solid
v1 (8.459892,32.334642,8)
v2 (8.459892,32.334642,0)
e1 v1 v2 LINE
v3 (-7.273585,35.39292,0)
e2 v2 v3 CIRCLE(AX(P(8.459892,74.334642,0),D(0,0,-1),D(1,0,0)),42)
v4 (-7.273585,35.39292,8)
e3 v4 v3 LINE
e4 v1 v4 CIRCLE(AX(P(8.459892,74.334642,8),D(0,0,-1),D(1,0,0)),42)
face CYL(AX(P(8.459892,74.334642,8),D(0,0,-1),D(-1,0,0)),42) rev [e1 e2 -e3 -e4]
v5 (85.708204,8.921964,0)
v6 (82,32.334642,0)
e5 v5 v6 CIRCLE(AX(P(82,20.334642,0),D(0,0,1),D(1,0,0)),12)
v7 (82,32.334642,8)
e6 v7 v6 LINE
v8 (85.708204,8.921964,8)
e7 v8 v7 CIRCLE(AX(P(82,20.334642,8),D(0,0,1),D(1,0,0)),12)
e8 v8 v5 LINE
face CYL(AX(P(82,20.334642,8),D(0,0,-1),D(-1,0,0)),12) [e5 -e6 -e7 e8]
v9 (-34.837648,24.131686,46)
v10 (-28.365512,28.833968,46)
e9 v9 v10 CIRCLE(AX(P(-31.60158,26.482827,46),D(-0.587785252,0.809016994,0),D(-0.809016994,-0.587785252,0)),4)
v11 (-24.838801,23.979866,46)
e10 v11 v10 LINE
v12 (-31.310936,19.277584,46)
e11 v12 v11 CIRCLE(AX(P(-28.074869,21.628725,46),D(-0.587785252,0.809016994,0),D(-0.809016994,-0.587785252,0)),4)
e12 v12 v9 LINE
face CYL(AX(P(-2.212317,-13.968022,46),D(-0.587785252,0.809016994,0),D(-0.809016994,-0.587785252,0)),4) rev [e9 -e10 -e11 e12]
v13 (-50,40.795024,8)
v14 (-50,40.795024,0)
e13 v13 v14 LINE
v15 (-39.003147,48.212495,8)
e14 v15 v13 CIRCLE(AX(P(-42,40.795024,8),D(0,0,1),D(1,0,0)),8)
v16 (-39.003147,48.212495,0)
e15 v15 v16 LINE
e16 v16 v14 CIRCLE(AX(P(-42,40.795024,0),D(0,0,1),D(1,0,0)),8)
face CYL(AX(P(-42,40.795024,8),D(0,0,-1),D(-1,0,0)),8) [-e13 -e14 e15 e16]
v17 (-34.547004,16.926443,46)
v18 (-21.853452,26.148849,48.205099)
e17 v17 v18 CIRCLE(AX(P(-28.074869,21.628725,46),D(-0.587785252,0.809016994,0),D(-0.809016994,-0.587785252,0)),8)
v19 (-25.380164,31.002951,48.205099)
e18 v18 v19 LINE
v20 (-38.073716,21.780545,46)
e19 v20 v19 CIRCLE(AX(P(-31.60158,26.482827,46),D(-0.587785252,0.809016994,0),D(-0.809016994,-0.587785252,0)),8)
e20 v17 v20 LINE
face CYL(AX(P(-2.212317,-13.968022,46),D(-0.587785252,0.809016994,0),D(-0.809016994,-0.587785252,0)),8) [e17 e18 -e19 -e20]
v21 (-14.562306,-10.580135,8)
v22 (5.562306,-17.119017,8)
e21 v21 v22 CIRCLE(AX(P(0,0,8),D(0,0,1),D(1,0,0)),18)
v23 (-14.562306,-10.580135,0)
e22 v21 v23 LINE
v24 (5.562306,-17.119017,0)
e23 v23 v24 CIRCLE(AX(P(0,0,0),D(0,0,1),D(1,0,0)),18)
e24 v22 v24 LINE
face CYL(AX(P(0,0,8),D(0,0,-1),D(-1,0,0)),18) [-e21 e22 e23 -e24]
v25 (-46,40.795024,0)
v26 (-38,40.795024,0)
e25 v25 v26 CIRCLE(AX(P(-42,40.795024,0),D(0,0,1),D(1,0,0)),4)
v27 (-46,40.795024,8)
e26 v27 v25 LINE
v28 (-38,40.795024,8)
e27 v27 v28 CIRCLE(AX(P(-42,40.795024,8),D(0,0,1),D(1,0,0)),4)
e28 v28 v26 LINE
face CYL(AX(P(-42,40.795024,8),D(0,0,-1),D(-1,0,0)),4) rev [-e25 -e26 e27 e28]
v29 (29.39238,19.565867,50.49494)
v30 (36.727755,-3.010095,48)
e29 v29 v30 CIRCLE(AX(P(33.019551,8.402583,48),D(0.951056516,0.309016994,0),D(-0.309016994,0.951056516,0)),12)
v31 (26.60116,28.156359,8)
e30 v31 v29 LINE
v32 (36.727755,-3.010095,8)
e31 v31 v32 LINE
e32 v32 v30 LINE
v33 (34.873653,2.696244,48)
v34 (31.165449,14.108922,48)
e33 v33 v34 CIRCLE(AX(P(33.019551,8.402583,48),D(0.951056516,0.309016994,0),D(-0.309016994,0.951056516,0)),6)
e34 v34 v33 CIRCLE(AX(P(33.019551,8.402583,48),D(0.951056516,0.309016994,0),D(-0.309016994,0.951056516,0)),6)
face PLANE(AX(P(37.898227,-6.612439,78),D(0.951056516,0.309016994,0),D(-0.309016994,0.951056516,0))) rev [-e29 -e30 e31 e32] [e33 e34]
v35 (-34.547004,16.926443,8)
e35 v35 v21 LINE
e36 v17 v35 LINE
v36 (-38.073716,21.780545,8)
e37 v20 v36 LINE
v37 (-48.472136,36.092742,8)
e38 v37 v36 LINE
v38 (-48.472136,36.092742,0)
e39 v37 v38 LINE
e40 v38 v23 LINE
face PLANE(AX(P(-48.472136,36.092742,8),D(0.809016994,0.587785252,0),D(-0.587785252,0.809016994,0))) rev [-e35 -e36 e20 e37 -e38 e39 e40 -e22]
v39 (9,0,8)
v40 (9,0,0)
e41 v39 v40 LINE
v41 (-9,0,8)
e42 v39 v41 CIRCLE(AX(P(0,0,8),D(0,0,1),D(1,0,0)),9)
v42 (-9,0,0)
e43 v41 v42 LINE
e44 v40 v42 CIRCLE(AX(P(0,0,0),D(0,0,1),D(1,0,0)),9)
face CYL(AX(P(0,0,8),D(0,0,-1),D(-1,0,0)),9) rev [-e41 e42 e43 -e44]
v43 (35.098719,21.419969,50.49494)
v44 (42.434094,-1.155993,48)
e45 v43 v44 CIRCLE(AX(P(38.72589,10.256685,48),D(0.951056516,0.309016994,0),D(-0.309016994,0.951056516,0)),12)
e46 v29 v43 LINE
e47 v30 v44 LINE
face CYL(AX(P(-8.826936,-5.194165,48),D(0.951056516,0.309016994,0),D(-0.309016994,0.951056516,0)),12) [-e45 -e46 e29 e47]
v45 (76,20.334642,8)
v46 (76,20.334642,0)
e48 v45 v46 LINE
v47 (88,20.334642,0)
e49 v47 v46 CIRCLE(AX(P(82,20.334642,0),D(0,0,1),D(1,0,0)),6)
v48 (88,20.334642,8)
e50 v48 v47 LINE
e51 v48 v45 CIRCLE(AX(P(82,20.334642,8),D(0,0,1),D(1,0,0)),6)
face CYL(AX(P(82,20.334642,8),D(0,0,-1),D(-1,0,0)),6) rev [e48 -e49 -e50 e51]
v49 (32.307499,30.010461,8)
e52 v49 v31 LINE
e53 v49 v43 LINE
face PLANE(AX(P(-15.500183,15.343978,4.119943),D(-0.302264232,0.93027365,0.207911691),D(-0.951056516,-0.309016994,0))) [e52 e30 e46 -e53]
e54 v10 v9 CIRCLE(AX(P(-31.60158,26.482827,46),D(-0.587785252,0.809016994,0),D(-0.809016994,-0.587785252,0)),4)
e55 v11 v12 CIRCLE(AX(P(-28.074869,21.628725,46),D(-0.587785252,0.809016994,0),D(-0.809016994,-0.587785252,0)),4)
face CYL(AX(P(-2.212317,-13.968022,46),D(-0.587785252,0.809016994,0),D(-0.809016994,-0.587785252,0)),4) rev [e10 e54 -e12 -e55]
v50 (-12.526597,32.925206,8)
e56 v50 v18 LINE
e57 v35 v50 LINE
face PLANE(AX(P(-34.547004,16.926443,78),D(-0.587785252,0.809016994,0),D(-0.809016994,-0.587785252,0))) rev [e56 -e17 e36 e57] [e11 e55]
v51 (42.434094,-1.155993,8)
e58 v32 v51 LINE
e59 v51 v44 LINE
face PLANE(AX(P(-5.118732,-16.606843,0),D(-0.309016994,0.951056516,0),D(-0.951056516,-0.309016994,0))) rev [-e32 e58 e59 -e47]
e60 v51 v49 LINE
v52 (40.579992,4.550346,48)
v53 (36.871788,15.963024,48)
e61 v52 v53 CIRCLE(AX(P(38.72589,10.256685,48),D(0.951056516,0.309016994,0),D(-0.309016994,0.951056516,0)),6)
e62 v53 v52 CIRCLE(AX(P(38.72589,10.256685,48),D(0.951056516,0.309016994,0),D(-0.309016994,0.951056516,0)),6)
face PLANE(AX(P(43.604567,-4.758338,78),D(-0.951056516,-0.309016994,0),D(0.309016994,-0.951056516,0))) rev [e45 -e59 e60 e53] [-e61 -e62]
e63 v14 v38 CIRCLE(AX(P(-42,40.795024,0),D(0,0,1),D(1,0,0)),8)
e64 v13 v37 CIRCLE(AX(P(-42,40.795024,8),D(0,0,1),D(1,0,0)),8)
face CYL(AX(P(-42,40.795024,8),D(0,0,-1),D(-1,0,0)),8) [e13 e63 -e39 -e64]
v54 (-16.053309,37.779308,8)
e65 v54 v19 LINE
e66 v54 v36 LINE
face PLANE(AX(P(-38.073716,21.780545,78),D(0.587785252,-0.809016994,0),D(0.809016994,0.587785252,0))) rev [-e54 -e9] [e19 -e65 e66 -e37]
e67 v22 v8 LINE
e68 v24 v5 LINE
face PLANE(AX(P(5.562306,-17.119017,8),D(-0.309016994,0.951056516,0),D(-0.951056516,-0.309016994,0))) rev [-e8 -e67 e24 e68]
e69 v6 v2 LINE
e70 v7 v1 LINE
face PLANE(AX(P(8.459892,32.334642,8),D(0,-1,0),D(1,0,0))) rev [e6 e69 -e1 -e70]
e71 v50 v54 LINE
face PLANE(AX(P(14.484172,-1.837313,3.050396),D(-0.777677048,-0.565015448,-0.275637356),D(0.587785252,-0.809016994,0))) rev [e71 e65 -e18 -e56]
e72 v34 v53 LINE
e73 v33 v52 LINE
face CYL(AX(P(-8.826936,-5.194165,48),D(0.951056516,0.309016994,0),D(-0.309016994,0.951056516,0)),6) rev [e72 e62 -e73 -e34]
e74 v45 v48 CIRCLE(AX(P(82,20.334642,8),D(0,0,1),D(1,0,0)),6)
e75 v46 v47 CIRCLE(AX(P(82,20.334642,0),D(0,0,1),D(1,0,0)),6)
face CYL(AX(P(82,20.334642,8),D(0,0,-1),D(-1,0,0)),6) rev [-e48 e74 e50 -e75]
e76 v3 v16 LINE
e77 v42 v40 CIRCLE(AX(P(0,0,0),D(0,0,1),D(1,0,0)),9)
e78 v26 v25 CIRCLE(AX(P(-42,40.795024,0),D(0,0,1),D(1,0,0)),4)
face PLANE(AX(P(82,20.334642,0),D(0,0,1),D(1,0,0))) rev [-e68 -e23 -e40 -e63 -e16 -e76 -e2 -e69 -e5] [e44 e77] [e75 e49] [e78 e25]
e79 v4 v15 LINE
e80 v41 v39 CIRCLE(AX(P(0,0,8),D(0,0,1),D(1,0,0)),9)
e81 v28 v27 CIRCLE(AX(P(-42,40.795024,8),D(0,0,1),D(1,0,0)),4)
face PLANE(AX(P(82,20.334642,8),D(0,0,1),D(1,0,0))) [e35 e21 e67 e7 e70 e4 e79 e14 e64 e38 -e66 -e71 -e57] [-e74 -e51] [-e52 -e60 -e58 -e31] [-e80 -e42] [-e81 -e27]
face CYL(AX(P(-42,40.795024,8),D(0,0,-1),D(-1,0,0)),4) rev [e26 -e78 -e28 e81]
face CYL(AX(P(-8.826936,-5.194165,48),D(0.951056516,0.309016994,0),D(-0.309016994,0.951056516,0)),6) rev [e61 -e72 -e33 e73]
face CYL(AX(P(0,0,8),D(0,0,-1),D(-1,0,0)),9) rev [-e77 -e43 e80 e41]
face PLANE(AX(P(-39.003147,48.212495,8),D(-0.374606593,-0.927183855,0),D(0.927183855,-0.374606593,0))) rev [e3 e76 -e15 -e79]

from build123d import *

# Parameters (mm, degrees)
BRACKET_PLATE_PROFILE_R    = 9
BRACKET_PLATE_PROFILE_R_2  = 4
BRACKET_PLATE_PROFILE_R_3  = 6
BRACKET_PLATE_8MM_DEPTH    = 8
ARMS_70MM_DEPTH            = 70
GUSSET_TAPER_CUT_PROFILE_R = 6
GUSSET_TAPER_CUT_DEPTH     = 50
ARM_TRIM_CUT_PROFILE_R     = 4
ARM_TRIM_CUT_DEPTH         = 50


with BuildPart() as part:
    # Bracket Plate Profile → Bracket Plate 8mm (new body)
    with BuildSketch(Plane.XY):
        with BuildLine():
            Line((-48.472135955, 36.092742474), (-14.562305899, -10.580134541))
            ThreePointArc((-14.562305899, -10.580134541), (-5.562305899, -17.119017293), (5.562305899, -17.119017293))
            Line((5.562305899, -17.119017293), (85.708203932, 8.92196355))
            ThreePointArc((85.708203932, 8.92196355), (93.852260087, 22.211855326), (82, 32.334641746))
            Line((82, 32.334641746), (8.459892396, 32.334641746))
            ThreePointArc((8.459892396, 32.334641746), (0.445914591, 33.106300041), (-7.273584527, 35.392919854))
            Line((-7.273584527, 35.392919854), (-39.003147253, 48.212495329))
            ThreePointArc((-39.003147253, 48.212495329), (-48.304086029, 45.720316295), (-48.472135955, 36.092742474))
        make_face()
        Circle(BRACKET_PLATE_PROFILE_R, mode=Mode.SUBTRACT)
        with Locations((-42, 40.795024493)):
            Circle(BRACKET_PLATE_PROFILE_R_2, mode=Mode.SUBTRACT)
        with Locations((82, 20.334641746)):
            Circle(BRACKET_PLATE_PROFILE_R_3, mode=Mode.SUBTRACT)
    extrude(amount=BRACKET_PLATE_8MM_DEPTH)

    # Arm Sections 34x6 → Arms 70mm (add)
    with BuildSketch(Plane.XY.offset(8)):
        Polygon((37.898227453, -6.612439485), (43.604566551, -4.758337518), (32.307498994, 30.01046132), (26.601159896, 28.156359354), align=None)
        Polygon((-38.07371599, 21.780545234), (-34.547004477, 16.926443267), (-12.049603456, 33.271761878), (-15.57631497, 38.125863845), align=None)
    extrude(amount=ARMS_70MM_DEPTH)

    # Gusset Taper Cut Profile → Gusset Taper Cut (cut)
    with BuildSketch(Plane(origin=(38.042260652, 12.360679775, 0), x_dir=(0, 0, -1), z_dir=(0.9510565162951532, 0.30901699437494873, 0))):
        with BuildLine():
            Line((-50.49494029, 9.525500165), (-8, 18.558078561))
            Line((-8, 18.558078561), (-78, 18.558078561))
            Line((-78, 18.558078561), (-78, -18))
            Line((-78, -18), (-8, -18))
            Line((-8, -18), (-8, -14.212271044))
            Line((-8, -14.212271044), (-48, -14.212271044))
            ThreePointArc((-48, -14.212271044), (-59.934262744, -3.466612603), (-50.49494029, 9.525500165))
        make_face()
        with Locations(Location((-48, -2.212271044, 0), (0, 0, 90))):
            Circle(GUSSET_TAPER_CUT_PROFILE_R)
    extrude(amount=-GUSSET_TAPER_CUT_DEPTH, mode=Mode.SUBTRACT)

    # Arm Trim Cut Profile → Arm Trim Cut (cut)
    with BuildSketch(Plane(origin=(-23.511410092, 32.360679775, 0), x_dir=(0.8090169943749487, 0.5877852522924716, 0), z_dir=(-0.5877852522924715, 0.8090169943749486, 0))):
        with Locations(Location((-10, -46, 0), (0, 0, 180))):
            Circle(ARM_TRIM_CUT_PROFILE_R)
        with BuildLine():
            Line((9.808316978, -8), (9.218720146, -8))
            Line((9.218720146, -8), (-2.309906432, -48.205098847))
            ThreePointArc((-2.309906432, -48.205098847), (-11.113384808, -53.92214455), (-18, -46))
            Line((-18, -46), (-18, -78))
            Line((-18, -78), (9.808316978, -78))
            Line((9.808316978, -78), (9.808316978, -8))
        make_face()
    extrude(amount=-ARM_TRIM_CUT_DEPTH, mode=Mode.SUBTRACT)


solid = part.part
